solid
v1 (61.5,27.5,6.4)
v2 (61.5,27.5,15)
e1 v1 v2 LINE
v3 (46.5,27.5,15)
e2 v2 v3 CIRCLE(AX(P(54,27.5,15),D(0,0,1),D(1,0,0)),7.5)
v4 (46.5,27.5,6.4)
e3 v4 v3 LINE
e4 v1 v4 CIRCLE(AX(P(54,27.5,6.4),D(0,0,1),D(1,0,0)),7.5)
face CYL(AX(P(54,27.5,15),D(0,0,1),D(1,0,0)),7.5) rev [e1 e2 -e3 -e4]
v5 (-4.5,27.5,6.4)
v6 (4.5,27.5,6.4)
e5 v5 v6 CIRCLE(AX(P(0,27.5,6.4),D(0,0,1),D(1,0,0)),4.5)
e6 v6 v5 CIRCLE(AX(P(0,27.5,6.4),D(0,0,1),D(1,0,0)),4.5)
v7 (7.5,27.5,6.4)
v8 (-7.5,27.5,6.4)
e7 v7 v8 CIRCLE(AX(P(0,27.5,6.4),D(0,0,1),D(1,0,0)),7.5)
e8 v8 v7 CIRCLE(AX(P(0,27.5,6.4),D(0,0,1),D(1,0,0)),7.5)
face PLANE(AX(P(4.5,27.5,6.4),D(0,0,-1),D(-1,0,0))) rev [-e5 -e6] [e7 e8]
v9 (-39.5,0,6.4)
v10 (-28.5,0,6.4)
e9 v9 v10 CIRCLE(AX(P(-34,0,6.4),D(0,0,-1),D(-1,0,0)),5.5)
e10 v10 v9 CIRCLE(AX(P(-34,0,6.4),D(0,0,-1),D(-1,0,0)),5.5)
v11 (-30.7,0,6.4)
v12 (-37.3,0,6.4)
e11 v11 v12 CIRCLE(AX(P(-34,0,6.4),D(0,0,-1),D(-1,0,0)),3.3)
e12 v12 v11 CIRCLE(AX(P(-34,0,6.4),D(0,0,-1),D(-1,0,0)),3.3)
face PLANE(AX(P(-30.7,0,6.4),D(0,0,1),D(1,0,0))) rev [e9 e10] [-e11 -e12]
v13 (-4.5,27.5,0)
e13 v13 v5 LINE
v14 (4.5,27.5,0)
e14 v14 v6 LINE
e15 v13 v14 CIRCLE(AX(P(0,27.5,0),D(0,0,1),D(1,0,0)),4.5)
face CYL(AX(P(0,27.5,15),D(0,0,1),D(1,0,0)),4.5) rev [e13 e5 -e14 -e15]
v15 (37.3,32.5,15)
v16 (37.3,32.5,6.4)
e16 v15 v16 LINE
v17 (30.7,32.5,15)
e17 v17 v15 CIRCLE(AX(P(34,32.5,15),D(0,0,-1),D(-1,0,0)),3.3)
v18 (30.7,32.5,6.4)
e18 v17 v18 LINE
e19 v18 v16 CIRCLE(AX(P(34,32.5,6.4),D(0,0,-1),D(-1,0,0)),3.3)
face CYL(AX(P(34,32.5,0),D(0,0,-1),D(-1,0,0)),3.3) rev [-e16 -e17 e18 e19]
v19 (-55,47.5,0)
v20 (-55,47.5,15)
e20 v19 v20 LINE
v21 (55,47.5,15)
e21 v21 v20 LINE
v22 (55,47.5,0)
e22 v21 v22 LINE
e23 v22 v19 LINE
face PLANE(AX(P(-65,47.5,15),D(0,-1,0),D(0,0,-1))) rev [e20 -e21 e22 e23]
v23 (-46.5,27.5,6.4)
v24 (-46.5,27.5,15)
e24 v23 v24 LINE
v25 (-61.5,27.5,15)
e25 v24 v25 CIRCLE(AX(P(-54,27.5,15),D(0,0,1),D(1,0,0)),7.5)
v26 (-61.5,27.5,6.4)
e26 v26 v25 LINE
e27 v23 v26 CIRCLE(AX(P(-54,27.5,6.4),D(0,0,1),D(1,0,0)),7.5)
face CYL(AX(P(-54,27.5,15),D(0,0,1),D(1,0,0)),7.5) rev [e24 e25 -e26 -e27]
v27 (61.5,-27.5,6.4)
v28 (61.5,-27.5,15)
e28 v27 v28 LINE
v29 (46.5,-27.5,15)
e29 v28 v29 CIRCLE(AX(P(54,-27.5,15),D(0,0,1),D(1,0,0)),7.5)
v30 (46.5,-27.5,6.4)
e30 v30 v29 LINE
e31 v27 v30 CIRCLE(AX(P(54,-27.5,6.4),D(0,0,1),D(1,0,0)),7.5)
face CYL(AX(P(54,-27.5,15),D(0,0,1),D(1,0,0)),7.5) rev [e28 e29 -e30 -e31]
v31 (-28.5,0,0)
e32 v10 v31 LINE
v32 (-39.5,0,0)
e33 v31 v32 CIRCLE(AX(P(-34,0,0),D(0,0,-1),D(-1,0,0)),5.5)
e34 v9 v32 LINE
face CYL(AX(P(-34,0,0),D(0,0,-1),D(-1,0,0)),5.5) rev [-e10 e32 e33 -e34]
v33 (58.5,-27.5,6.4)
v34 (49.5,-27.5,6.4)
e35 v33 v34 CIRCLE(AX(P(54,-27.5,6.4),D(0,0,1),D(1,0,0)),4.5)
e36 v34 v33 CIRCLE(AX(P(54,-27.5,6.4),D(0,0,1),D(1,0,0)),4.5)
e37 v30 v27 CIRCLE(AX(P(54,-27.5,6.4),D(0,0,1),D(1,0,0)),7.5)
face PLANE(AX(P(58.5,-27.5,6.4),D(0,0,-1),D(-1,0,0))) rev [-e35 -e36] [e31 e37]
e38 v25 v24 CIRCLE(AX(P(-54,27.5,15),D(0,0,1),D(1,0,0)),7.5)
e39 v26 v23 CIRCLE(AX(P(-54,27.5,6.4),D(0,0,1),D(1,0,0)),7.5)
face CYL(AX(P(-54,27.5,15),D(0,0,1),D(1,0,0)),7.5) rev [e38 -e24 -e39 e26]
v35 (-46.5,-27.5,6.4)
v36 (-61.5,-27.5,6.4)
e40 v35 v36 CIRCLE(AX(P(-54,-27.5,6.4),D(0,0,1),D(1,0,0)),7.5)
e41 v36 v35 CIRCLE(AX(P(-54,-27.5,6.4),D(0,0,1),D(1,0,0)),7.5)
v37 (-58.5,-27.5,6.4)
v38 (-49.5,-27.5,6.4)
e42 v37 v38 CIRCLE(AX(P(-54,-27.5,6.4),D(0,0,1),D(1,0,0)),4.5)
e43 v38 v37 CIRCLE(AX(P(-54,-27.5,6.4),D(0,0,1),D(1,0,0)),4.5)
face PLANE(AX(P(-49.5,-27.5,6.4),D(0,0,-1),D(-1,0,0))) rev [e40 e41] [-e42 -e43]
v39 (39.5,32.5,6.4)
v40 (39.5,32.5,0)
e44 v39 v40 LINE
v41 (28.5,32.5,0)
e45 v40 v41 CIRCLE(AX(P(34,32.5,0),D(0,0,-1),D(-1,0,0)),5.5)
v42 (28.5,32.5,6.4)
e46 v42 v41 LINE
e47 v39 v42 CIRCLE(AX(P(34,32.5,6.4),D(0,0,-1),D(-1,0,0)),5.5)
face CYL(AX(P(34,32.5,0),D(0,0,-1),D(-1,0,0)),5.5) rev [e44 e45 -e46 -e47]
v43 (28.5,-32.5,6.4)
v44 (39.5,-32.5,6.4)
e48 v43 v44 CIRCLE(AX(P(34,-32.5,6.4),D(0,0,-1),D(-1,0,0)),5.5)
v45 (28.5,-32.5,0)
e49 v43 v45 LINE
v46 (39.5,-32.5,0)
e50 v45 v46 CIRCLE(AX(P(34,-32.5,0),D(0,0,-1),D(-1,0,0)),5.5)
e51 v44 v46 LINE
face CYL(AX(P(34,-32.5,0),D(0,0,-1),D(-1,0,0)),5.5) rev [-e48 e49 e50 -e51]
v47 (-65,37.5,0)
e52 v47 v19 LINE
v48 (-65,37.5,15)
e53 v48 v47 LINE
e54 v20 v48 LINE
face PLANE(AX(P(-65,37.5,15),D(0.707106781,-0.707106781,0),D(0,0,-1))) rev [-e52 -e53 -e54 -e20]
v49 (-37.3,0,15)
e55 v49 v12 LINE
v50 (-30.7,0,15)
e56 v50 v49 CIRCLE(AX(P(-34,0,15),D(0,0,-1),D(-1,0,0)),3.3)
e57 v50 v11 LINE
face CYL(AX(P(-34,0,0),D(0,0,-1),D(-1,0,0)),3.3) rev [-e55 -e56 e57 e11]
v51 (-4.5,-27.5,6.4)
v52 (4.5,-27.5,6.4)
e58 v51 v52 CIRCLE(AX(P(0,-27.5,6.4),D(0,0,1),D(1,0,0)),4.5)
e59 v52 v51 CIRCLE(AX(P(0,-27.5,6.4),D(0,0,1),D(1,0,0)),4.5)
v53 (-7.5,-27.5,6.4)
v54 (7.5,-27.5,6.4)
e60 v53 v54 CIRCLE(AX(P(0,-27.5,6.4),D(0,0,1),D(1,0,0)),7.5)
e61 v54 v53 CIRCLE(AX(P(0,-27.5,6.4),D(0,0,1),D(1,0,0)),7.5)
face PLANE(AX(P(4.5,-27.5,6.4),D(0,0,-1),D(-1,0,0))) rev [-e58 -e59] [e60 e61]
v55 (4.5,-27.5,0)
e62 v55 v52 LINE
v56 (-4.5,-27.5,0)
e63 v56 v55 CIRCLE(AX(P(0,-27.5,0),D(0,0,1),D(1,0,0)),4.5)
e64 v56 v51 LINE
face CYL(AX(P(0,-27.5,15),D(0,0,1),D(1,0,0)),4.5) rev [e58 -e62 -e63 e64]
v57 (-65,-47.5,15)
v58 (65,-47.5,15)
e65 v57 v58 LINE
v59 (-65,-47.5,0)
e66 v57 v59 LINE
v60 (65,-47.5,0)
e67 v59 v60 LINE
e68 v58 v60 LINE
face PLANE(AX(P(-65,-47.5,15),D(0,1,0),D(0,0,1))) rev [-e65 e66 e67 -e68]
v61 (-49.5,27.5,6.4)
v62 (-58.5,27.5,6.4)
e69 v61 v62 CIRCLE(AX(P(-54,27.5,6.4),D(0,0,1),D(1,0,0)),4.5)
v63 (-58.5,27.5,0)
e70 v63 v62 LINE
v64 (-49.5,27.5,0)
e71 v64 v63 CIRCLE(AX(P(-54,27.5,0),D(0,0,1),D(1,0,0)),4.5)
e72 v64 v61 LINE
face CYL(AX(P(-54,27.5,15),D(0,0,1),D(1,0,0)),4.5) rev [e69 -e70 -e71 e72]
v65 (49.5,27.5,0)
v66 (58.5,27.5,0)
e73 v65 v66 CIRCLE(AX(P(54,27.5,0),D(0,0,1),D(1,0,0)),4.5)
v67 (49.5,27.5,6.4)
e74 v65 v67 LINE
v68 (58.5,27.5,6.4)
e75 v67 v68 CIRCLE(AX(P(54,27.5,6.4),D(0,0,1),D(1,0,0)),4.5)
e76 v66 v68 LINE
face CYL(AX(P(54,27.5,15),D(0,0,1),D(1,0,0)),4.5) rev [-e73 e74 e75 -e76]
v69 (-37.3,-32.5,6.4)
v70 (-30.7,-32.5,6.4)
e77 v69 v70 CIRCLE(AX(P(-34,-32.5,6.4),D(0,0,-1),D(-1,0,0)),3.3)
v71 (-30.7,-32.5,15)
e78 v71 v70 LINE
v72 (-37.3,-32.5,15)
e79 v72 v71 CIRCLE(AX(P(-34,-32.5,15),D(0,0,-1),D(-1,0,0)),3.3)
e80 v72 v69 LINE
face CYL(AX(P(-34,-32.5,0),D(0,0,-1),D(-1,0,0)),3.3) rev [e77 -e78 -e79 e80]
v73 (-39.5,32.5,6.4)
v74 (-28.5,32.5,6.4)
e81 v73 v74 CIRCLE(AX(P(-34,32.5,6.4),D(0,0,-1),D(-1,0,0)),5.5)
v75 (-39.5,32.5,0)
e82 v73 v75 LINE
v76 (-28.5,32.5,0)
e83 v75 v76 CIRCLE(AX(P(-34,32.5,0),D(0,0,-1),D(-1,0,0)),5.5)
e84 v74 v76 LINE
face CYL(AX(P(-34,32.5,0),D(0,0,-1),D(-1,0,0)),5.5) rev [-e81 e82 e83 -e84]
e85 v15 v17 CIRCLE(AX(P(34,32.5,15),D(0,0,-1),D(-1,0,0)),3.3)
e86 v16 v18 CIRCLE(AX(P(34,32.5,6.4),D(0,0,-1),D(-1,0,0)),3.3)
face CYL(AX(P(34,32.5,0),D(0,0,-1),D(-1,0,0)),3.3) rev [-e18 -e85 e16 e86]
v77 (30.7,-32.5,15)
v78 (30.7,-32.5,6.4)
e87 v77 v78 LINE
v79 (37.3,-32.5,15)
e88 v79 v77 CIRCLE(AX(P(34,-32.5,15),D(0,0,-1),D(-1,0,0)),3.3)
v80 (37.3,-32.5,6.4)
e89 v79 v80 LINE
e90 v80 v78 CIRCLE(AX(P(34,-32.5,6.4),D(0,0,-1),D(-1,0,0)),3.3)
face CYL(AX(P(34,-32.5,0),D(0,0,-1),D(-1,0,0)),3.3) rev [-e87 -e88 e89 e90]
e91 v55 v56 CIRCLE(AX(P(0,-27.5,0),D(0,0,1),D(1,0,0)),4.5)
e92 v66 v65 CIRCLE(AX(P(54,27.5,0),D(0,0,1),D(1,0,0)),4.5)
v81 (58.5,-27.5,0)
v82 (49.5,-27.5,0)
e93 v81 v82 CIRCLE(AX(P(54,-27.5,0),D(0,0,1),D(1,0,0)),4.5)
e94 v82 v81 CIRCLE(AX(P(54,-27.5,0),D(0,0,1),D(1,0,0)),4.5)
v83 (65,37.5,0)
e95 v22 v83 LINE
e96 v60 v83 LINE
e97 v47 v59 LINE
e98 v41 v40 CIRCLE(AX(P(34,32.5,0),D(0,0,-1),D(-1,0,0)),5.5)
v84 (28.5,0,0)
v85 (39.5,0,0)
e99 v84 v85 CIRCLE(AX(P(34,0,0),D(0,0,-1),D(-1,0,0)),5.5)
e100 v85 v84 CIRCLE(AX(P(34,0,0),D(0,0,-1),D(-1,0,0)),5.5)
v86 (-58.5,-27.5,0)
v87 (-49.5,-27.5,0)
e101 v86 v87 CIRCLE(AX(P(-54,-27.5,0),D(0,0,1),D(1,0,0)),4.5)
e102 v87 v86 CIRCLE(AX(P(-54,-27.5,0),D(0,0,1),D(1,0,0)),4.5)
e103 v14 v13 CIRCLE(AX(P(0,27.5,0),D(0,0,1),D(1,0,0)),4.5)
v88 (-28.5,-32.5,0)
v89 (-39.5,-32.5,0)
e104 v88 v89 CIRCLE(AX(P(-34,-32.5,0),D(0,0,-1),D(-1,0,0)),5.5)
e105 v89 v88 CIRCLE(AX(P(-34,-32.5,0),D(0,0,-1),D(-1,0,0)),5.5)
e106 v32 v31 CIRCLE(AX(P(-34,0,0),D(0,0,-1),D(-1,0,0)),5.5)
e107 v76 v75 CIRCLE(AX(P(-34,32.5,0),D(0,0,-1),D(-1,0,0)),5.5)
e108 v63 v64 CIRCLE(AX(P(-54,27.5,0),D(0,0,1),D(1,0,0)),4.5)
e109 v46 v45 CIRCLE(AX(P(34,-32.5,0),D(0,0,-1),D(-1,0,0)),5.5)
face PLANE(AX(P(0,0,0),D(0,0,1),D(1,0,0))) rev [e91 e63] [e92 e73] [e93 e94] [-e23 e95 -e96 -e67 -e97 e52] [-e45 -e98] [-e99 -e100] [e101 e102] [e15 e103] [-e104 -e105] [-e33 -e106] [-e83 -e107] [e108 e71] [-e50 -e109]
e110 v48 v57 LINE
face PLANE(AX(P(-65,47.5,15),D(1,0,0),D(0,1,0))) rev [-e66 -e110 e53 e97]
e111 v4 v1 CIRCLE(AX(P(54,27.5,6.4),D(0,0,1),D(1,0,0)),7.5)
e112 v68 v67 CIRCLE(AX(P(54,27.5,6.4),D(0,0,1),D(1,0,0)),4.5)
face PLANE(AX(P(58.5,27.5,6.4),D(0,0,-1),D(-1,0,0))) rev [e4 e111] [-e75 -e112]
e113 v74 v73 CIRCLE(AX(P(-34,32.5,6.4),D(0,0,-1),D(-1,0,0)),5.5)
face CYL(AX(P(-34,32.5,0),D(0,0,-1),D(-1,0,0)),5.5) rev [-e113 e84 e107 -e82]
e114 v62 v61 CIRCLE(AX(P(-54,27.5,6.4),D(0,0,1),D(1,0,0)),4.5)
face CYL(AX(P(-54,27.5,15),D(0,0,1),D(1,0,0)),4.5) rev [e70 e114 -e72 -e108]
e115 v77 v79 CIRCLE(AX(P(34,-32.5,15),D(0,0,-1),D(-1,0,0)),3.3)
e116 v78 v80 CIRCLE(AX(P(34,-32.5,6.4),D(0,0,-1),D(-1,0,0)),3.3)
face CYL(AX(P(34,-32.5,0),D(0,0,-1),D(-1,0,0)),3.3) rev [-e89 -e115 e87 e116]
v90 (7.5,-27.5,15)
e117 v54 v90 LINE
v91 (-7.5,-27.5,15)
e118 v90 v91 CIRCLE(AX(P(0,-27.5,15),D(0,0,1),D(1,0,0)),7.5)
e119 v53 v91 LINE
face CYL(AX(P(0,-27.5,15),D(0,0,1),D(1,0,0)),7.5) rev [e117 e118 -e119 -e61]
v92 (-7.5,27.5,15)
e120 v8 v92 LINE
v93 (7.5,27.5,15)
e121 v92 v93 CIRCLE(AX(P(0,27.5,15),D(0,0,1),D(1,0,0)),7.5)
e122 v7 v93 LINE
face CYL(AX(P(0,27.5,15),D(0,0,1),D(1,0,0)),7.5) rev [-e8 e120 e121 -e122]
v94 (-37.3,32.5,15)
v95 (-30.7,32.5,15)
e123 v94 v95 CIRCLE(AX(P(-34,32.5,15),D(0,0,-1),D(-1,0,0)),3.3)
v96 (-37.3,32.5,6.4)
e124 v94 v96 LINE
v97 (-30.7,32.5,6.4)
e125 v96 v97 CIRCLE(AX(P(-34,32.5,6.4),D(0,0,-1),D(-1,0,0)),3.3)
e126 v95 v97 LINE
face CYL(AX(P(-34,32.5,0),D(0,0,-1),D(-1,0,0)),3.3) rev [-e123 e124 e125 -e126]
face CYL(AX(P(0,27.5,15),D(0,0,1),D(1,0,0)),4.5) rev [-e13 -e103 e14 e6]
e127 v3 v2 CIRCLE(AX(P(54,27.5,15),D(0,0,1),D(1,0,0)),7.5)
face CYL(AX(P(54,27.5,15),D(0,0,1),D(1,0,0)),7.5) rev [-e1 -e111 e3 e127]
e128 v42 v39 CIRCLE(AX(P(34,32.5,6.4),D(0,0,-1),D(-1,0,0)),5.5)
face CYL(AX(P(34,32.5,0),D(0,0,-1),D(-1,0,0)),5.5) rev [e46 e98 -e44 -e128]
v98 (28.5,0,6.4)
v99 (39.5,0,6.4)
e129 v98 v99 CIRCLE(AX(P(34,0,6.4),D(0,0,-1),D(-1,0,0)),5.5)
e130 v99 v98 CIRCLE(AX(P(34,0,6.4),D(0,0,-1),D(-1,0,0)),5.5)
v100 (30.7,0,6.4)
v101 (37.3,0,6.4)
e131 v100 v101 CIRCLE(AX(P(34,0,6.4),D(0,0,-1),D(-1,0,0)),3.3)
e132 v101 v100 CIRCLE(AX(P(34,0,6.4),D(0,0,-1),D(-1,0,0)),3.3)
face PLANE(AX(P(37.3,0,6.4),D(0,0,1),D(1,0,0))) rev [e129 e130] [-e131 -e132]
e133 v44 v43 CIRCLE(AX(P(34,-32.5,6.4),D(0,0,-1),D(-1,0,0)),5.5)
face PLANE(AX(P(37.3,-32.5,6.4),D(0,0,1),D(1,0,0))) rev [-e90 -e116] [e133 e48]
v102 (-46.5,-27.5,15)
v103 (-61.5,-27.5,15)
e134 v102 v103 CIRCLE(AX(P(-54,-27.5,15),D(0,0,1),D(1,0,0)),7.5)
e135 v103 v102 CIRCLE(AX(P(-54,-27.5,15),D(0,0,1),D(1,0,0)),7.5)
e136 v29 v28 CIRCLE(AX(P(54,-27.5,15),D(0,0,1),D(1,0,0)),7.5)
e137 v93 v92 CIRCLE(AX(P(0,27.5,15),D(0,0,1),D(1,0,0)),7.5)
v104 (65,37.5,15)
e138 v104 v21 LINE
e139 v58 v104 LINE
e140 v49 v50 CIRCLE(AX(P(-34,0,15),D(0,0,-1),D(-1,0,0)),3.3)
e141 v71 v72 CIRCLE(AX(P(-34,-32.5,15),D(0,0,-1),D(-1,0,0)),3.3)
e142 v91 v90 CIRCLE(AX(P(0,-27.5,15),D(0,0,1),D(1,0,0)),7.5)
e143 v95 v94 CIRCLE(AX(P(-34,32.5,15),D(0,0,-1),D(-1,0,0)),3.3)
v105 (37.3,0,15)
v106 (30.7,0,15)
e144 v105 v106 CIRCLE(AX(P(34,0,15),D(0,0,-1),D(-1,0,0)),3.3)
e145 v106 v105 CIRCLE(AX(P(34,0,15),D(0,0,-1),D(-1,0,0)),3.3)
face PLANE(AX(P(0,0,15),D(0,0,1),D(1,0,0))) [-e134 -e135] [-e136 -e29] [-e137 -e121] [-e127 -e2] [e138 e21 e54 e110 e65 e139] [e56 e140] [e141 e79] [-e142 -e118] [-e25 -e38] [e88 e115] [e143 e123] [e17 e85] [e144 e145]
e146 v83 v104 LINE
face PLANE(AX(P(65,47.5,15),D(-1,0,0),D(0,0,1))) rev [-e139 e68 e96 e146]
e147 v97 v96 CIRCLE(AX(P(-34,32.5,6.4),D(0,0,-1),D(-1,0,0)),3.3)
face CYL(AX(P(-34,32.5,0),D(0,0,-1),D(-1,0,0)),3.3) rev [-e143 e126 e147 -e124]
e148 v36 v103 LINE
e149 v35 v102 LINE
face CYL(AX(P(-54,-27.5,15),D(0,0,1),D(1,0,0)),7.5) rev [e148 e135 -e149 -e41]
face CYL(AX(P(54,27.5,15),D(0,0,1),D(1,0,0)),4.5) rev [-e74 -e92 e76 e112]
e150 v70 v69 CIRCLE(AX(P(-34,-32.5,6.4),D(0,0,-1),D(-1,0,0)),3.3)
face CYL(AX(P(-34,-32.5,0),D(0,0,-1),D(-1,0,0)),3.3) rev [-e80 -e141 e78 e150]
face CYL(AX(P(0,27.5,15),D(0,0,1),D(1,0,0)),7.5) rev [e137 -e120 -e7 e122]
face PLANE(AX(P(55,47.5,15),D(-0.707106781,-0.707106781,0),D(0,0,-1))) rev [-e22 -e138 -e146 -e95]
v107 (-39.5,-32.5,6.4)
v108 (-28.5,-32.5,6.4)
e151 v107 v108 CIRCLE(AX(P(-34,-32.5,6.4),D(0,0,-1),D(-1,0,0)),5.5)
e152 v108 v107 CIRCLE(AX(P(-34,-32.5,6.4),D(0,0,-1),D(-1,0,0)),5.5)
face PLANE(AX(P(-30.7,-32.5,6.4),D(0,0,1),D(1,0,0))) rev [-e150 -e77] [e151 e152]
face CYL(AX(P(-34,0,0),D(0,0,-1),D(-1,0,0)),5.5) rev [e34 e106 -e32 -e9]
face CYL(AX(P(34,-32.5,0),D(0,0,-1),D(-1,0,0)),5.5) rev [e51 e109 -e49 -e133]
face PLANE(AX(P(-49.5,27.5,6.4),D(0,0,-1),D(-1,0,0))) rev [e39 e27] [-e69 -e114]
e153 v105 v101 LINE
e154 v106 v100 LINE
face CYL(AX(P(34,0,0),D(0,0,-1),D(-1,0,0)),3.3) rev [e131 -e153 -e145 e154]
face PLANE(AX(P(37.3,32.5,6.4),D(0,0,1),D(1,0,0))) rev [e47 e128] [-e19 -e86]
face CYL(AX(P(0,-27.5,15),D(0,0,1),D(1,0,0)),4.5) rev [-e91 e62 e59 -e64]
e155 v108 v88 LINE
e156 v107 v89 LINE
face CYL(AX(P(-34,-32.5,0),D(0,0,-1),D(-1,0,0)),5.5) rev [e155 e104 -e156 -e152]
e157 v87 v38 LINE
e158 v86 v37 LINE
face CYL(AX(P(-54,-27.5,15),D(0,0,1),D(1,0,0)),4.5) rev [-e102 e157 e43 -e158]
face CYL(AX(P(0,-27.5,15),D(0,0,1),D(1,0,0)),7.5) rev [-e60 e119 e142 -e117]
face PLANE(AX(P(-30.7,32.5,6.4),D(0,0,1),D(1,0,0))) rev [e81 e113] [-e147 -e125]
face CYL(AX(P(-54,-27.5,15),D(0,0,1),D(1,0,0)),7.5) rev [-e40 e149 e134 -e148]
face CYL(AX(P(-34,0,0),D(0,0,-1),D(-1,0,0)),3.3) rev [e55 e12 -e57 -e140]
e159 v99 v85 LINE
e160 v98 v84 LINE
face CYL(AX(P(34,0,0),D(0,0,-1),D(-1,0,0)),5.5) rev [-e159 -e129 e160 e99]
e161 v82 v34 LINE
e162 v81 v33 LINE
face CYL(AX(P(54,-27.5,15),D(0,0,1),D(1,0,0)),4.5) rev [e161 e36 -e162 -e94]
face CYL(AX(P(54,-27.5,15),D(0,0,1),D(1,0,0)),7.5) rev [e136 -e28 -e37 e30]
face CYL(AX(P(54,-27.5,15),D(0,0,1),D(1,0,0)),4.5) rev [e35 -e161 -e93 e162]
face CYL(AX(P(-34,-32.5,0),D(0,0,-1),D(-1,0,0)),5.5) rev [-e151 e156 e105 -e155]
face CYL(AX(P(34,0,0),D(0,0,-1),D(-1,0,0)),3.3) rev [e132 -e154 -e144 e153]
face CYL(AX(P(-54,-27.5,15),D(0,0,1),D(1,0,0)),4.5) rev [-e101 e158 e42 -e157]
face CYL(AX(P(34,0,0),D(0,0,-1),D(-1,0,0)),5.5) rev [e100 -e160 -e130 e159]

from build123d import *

# Parameters (mm, degrees)
SKETCH1_W                                           = 130
SKETCH1_H                                           = 95
BOSS_EXTRUDE1_DEPTH                                 = 15
CBORE_FOR_M8_HEX_SOCKET_HEAD_CAP_SCREW1_D           = 9
CBORE_FOR_M8_HEX_SOCKET_HEAD_CAP_SCREW1_CBORE_D     = 15
CBORE_FOR_M8_HEX_SOCKET_HEAD_CAP_SCREW1_CBORE_DEPTH = 8.6
CHAMFER1_SIZE                                       = 10
CBORE_FOR_M6_HEX_SOCKET_HEAD_CAP_SCREW1_D           = 6.6
CBORE_FOR_M6_HEX_SOCKET_HEAD_CAP_SCREW1_CBORE_D     = 11
CBORE_FOR_M6_HEX_SOCKET_HEAD_CAP_SCREW1_CBORE_DEPTH = 6.4


with BuildPart() as part:
    # Sketch1 → Boss-Extrude1 (new body)
    with BuildSketch(Plane.XY):
        Rectangle(SKETCH1_W, SKETCH1_H)
    extrude(amount=BOSS_EXTRUDE1_DEPTH)

    # CBORE for M8 Hex Socket Head Cap Screw1 (through all)
    with Locations(Plane.XY.offset(15)):
        with Locations((54, 27.5), (54, -27.5), (-54, 27.5), (-54, -27.5), (0, 27.5), (0, -27.5)):
            CounterBoreHole(CBORE_FOR_M8_HEX_SOCKET_HEAD_CAP_SCREW1_D / 2, CBORE_FOR_M8_HEX_SOCKET_HEAD_CAP_SCREW1_CBORE_D / 2, CBORE_FOR_M8_HEX_SOCKET_HEAD_CAP_SCREW1_CBORE_DEPTH)

    # Chamfer1
    chamfer1_edges = [part.edges().sort_by_distance(p)[0] for p in [
        (-65, 47.5, 7.5),
        (65, 47.5, 7.5),
    ]]
    chamfer(chamfer1_edges, length=CHAMFER1_SIZE)

    # CBORE for M6 Hex Socket Head Cap Screw1 (through all)
    with Locations(Plane(origin=(0, 0, 0), x_dir=(-1, 0, 0), z_dir=(0, 0, -1))):
        with Locations((-34, -32.5), (-34, 0), (-34, 32.5), (34, -32.5), (34, 0), (34, 32.5)):
            CounterBoreHole(CBORE_FOR_M6_HEX_SOCKET_HEAD_CAP_SCREW1_D / 2, CBORE_FOR_M6_HEX_SOCKET_HEAD_CAP_SCREW1_CBORE_D / 2, CBORE_FOR_M6_HEX_SOCKET_HEAD_CAP_SCREW1_CBORE_DEPTH)


solid = part.part
